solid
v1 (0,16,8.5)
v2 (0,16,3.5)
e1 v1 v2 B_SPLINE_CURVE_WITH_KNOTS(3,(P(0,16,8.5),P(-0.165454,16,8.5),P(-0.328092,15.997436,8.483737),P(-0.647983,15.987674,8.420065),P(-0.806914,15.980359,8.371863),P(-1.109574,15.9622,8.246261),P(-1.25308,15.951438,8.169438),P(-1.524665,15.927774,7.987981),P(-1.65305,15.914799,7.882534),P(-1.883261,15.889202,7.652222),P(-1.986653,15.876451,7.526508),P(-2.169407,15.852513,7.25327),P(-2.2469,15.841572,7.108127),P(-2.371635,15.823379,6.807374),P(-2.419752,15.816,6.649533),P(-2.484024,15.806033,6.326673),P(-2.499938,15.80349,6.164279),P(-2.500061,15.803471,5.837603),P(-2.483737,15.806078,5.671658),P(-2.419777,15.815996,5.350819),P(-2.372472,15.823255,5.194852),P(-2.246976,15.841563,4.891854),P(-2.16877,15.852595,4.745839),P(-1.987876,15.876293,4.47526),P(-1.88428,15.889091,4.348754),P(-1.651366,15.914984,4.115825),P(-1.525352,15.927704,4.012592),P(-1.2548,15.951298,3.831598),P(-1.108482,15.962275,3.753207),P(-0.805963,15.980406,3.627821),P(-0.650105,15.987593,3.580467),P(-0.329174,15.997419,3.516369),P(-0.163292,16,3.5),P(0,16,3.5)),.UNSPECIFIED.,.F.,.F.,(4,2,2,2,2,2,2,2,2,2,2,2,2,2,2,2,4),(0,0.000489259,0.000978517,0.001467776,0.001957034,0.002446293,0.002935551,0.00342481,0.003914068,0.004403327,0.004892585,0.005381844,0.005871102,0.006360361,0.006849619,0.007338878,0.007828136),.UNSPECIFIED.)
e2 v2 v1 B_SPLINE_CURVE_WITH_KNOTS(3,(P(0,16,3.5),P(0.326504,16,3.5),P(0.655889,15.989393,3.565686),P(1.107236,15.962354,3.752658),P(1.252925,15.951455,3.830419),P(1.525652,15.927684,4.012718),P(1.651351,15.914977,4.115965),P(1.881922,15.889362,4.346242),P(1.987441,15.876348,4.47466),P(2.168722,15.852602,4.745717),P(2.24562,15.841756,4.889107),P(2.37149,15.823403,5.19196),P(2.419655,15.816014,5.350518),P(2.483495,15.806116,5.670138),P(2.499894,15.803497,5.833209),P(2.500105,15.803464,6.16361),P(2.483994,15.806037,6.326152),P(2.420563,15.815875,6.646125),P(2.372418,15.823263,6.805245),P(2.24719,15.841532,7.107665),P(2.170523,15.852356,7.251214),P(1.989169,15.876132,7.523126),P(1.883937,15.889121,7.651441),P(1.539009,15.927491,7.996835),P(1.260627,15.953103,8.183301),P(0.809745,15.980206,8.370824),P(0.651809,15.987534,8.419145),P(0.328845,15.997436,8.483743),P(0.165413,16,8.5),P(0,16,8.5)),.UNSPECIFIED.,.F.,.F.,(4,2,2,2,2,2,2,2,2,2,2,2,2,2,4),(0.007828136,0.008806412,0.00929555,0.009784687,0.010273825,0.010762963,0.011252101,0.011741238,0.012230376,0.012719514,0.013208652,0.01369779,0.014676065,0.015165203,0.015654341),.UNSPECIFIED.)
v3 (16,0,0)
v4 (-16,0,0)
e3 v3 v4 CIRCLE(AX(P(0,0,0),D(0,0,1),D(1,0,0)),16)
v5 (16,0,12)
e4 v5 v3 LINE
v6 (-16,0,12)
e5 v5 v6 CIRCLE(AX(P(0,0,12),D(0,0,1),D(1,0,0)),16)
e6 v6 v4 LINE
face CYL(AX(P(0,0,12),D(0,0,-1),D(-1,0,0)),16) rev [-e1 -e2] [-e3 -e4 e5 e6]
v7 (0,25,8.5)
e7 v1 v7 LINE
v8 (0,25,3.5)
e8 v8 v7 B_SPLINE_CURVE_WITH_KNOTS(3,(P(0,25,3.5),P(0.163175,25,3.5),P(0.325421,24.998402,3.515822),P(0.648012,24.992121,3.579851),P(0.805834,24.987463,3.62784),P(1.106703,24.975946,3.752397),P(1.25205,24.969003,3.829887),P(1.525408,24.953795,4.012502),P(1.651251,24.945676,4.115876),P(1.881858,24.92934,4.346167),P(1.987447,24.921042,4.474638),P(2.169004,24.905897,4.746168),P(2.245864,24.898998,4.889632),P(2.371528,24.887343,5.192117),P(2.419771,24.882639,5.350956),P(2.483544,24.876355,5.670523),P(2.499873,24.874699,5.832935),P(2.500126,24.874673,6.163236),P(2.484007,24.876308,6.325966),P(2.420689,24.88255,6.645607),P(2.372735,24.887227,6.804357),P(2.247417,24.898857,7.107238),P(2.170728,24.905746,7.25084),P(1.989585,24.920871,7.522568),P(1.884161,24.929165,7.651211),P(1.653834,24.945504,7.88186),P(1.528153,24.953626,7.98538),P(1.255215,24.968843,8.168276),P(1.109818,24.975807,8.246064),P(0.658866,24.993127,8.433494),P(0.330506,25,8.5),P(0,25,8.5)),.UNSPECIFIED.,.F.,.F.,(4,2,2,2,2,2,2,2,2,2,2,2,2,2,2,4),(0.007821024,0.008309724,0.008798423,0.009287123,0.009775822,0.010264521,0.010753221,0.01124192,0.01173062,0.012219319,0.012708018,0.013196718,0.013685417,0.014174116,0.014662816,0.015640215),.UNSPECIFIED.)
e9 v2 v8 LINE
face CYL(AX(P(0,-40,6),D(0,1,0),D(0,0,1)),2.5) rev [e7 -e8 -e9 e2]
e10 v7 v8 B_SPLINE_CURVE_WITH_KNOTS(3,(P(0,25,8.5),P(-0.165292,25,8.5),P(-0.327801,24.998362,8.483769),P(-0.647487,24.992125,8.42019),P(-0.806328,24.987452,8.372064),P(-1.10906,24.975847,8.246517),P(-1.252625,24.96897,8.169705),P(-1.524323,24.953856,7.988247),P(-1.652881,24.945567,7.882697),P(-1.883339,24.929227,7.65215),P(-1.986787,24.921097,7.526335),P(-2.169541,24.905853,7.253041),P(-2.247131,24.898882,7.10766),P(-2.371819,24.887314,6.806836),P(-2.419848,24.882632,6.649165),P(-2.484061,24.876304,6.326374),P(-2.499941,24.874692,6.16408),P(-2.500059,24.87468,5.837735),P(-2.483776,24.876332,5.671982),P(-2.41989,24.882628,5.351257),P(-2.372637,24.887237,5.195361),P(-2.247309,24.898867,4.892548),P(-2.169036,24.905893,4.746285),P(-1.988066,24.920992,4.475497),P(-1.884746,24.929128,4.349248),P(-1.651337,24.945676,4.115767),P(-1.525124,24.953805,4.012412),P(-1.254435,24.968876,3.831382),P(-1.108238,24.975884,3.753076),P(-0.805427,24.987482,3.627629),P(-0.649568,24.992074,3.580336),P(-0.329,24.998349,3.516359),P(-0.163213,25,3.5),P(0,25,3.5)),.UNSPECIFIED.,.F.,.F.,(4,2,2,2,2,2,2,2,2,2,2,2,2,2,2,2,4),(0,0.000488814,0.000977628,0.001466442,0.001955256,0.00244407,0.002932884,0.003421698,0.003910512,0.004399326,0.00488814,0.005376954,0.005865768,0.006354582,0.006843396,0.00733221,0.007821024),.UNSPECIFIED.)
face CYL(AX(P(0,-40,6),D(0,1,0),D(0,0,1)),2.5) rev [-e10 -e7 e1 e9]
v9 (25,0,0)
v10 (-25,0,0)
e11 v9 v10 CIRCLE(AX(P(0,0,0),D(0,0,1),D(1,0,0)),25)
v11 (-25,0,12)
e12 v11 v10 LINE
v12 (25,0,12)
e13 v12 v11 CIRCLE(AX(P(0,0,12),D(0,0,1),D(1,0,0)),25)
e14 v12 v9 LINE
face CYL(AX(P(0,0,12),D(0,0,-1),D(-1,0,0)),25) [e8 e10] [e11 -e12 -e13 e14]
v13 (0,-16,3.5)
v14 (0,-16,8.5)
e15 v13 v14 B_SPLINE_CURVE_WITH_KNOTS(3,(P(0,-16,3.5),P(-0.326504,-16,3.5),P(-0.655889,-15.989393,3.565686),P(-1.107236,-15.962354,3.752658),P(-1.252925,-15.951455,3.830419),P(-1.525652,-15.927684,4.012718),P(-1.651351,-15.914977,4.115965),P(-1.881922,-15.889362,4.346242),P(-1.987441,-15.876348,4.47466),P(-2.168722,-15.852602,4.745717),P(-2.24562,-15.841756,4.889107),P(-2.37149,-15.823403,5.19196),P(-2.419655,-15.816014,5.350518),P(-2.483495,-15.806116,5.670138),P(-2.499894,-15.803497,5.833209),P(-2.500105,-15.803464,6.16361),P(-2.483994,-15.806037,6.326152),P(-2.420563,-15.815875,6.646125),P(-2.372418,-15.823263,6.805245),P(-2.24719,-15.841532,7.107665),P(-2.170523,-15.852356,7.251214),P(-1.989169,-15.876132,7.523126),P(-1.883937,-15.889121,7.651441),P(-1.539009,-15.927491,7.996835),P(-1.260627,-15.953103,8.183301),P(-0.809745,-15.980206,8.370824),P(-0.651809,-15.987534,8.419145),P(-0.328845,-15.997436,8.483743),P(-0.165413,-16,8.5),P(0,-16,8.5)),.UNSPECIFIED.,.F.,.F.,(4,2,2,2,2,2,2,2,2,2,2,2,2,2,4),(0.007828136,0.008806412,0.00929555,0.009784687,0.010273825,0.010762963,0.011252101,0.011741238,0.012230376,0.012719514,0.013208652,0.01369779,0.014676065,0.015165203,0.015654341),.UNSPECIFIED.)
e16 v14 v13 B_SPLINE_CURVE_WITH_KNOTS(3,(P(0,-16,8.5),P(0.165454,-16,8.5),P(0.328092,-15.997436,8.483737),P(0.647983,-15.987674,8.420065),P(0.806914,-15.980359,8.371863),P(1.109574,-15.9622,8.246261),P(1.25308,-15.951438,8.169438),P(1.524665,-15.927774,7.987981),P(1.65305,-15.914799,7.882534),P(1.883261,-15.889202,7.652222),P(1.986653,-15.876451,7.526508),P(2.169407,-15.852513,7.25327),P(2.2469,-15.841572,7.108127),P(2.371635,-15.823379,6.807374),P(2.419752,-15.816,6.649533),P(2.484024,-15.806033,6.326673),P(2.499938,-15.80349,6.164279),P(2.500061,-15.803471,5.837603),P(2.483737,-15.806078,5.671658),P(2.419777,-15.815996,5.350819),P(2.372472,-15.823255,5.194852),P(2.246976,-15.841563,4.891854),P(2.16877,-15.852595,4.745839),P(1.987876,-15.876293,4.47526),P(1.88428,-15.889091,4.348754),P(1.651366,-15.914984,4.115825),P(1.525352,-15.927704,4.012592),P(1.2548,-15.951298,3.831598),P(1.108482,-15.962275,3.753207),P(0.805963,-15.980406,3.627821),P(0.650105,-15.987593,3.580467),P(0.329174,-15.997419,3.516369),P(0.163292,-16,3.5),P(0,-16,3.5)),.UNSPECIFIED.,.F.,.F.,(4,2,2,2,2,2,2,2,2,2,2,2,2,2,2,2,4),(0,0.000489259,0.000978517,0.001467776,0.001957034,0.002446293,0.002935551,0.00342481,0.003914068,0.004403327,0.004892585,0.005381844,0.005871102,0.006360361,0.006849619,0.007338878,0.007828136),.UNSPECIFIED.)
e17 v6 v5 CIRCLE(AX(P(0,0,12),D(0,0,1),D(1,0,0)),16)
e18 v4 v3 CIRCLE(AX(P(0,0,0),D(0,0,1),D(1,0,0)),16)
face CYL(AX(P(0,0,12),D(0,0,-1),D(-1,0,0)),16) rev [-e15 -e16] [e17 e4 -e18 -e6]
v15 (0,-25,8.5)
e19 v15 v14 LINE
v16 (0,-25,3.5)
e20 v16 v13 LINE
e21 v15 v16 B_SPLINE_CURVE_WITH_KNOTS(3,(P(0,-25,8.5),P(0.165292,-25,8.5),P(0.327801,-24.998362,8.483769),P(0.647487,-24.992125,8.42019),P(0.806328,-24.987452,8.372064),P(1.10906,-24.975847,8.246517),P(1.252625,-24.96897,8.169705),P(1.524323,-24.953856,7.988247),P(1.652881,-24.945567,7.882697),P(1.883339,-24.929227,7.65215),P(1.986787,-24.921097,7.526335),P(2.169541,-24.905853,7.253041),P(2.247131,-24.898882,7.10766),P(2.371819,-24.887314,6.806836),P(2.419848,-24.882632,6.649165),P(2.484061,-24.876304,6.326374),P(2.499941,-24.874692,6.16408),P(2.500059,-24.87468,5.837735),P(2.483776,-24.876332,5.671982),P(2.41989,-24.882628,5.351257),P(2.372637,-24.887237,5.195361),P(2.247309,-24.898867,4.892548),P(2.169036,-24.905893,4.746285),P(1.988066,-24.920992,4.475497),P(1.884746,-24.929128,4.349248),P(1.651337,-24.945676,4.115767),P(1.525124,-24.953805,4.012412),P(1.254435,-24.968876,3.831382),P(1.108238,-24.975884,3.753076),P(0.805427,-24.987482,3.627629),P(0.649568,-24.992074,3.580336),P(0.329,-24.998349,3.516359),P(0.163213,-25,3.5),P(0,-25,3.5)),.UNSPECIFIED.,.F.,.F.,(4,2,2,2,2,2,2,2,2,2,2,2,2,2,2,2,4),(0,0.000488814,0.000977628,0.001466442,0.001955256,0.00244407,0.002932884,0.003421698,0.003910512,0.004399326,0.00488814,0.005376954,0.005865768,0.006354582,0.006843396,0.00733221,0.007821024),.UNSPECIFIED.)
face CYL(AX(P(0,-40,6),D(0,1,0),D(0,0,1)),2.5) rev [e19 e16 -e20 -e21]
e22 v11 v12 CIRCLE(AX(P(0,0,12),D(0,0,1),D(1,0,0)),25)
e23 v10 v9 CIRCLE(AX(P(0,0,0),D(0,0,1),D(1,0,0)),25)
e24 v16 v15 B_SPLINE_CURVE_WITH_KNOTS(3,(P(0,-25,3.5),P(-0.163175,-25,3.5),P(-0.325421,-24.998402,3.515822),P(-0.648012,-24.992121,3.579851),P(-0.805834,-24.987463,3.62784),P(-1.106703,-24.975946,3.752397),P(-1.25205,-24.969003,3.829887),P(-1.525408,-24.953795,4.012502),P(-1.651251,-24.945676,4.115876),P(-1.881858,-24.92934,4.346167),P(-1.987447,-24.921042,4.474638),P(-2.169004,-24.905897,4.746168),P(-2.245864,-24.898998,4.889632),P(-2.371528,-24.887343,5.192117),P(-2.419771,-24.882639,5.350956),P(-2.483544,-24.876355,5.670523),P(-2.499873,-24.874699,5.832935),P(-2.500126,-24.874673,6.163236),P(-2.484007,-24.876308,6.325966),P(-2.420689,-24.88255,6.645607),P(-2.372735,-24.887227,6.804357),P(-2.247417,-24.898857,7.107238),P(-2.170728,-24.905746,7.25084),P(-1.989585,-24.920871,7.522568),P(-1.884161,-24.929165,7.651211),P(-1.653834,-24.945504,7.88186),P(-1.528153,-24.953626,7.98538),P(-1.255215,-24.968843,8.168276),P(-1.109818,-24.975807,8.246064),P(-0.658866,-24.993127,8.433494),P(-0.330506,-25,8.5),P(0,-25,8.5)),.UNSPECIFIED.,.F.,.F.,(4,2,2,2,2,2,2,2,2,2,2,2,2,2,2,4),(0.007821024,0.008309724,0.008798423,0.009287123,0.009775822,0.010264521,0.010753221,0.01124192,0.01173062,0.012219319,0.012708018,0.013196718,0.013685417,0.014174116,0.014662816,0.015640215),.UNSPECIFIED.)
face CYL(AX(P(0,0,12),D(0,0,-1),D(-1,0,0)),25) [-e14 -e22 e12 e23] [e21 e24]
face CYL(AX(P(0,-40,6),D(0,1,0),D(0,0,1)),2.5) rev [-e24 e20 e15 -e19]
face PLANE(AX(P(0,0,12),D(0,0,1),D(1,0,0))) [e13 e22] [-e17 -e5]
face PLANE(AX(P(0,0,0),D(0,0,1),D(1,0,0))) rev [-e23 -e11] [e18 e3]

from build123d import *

# Parameters (mm, degrees)
COLLAR_RING_PROFILE_R          = 25
COLLAR_RING_PROFILE_R_2        = 16
COLLAR_RING_OD50XID32X12_DEPTH = 12
CROSS_HOLE_SKETCH_R            = 2.5
CROSS_HOLE_5_DEPTH             = 40


with BuildPart() as part:
    # Collar Ring Profile → Collar Ring OD50xID32x12 (new body)
    with BuildSketch(Plane.XY):
        Circle(COLLAR_RING_PROFILE_R)
        Circle(COLLAR_RING_PROFILE_R_2, mode=Mode.SUBTRACT)
    extrude(amount=COLLAR_RING_OD50XID32X12_DEPTH)

    # Cross Hole Sketch → Cross Hole Ø5 (cut, symmetric)
    with BuildSketch(Plane(origin=(0, 0, 0), x_dir=(1, 0, 0), z_dir=(0, 1, 0))):
        with Locations(Location((0, -6, 0), (0, 0, 270))):
            Circle(CROSS_HOLE_SKETCH_R)
    extrude(amount=CROSS_HOLE_5_DEPTH, both=True, mode=Mode.SUBTRACT)


solid = part.part
